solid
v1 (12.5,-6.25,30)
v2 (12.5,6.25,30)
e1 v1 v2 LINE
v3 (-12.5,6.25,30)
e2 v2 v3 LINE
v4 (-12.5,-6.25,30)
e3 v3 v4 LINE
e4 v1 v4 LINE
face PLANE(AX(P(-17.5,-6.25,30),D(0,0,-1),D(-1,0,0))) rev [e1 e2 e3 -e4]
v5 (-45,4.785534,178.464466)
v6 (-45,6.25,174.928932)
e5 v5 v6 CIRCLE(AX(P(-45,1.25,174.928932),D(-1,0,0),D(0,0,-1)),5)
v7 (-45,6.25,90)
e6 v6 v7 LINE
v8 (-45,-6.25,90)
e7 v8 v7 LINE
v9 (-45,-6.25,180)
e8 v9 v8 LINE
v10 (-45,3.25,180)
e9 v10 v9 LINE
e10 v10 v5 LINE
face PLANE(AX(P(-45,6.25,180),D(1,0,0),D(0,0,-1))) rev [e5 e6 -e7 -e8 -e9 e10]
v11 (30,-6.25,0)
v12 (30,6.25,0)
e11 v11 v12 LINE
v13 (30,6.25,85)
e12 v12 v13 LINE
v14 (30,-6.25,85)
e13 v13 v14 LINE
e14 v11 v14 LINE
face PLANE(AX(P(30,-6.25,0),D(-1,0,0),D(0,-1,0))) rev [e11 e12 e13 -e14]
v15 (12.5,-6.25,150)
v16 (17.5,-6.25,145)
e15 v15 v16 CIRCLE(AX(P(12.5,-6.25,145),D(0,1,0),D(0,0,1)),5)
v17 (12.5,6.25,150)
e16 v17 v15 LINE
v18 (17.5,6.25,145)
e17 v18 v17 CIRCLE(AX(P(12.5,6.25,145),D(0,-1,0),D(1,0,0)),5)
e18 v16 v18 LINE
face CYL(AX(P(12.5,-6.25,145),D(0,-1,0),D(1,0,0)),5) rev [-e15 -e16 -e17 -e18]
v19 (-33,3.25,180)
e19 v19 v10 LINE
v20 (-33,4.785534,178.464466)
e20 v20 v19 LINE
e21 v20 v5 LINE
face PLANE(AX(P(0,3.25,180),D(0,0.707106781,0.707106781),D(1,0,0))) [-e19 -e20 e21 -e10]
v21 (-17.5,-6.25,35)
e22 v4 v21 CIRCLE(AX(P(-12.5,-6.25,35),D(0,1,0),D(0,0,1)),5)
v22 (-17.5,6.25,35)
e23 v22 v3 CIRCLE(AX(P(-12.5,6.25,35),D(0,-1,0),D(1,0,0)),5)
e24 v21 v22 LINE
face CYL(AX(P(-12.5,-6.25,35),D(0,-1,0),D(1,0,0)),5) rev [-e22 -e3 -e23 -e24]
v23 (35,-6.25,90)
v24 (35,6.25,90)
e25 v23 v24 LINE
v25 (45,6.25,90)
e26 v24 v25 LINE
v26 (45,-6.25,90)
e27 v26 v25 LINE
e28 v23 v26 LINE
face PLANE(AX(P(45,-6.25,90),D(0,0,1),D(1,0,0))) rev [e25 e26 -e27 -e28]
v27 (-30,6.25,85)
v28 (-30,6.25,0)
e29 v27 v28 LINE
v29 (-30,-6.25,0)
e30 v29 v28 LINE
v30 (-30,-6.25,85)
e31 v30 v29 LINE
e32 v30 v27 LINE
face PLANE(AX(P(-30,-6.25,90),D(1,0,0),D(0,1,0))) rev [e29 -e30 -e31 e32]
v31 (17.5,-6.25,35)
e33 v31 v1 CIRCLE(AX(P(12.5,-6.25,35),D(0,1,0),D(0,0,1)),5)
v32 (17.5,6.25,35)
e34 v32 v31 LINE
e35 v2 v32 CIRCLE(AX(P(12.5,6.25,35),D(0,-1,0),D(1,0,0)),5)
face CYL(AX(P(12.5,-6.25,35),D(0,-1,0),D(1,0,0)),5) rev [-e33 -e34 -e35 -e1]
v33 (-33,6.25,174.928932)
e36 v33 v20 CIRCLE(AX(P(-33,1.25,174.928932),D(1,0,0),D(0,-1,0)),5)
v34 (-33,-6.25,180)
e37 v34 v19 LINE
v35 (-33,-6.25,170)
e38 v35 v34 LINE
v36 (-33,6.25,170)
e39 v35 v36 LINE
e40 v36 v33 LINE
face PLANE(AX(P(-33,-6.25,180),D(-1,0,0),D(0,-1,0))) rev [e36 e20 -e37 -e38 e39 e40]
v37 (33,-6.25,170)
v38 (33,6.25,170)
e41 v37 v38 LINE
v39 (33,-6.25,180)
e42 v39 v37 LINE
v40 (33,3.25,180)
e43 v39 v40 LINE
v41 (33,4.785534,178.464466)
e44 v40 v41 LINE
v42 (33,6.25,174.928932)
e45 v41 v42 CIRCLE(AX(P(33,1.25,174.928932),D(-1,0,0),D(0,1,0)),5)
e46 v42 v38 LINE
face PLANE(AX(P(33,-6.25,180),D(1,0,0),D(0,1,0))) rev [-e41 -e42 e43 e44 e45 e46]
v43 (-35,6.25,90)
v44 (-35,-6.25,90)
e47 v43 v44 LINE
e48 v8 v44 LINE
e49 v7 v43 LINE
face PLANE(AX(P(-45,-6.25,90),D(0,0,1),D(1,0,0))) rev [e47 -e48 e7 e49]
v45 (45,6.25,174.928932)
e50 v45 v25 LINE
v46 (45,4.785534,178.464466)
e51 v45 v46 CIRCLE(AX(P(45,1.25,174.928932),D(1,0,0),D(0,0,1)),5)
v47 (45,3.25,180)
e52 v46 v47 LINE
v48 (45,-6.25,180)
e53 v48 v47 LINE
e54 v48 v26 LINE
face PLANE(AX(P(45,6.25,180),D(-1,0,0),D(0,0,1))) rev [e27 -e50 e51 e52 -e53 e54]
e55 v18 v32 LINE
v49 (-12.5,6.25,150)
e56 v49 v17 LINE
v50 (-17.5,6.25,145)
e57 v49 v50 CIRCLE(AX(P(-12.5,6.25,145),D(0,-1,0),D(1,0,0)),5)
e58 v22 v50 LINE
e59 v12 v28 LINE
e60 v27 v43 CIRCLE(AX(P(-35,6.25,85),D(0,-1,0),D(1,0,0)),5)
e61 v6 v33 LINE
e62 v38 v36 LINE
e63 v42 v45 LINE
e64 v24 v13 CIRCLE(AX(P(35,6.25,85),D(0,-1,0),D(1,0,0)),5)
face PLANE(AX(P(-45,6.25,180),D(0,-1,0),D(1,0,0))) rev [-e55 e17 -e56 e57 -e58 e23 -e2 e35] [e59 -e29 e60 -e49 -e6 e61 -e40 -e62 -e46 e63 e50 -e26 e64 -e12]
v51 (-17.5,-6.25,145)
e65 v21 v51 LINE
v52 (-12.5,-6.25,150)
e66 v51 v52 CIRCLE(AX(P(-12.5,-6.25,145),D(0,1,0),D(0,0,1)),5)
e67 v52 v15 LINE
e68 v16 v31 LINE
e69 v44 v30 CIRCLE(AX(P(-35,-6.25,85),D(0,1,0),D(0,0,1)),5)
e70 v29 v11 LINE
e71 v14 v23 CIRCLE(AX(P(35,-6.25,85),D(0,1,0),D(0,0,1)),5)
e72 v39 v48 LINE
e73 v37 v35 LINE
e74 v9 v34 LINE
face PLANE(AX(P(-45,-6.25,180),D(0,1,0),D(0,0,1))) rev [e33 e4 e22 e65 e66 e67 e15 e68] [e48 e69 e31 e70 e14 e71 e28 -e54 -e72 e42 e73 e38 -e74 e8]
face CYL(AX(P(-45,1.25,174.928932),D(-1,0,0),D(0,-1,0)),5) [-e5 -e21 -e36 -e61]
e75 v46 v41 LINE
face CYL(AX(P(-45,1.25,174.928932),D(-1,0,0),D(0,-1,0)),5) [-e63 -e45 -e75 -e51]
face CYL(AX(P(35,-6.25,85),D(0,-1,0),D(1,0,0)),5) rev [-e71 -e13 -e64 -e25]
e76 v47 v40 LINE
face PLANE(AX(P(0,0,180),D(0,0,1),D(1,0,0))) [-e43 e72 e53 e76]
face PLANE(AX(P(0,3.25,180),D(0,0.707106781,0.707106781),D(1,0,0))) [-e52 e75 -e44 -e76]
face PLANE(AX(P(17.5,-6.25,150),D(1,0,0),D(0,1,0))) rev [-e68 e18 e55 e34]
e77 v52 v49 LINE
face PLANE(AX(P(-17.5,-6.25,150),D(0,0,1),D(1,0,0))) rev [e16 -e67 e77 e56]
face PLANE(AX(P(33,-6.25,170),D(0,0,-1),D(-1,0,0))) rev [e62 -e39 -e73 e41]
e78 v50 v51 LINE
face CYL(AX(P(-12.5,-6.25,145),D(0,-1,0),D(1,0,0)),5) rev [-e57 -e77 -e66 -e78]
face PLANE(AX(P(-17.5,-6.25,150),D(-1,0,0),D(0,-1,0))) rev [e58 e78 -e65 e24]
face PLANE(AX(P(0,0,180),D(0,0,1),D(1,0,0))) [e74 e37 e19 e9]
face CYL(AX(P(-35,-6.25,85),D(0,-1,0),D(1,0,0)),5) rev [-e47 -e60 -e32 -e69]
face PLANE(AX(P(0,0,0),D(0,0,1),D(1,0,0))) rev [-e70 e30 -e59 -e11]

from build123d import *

# Parameters (mm, degrees)
SKETCH1_W           = 90
SKETCH1_H           = 12.5
BOSS_EXTRUDE1_DEPTH = 180
SKETCH2_W           = 66
SKETCH2_H           = 10
CUT_EXTRUDE1_DEPTH  = 186.960345235
CHAMFER1_SIZE       = 3
FILLET1_R           = 5
SKETCH3_W           = 15
SKETCH3_H           = 90
CUT_EXTRUDE2_DEPTH  = 186.960345235
SKETCH4_W           = 35
SKETCH4_H           = 120
CUT_EXTRUDE3_DEPTH  = 186.960345235
FILLET2_R           = 5
FILLET3_R           = 5


with BuildPart() as part:
    # Sketch1 → Boss-Extrude1 (new body)
    with BuildSketch(Plane.XY):
        Rectangle(SKETCH1_W, SKETCH1_H)
    extrude(amount=BOSS_EXTRUDE1_DEPTH)

    # Sketch2 → Cut-Extrude1 (cut, through all)
    with BuildSketch(Plane(origin=(0, 6.25, 0), x_dir=(1, 0, 0), z_dir=(0, 1, 0))):
        with Locations((0, -175)):
            Rectangle(SKETCH2_W, SKETCH2_H)
    extrude(amount=-CUT_EXTRUDE1_DEPTH, mode=Mode.SUBTRACT)

    # Chamfer1
    chamfer1_edges = [part.edges().sort_by_distance(p)[0] for p in [
        (39, 6.25, 180),
        (-39, 6.25, 180),
    ]]
    chamfer(chamfer1_edges, length=CHAMFER1_SIZE)

    # Fillet1
    fillet1_edges = [part.edges().sort_by_distance(p)[0] for p in [
        (39, 6.25, 177),
        (-39, 6.25, 177),
    ]]
    fillet(fillet1_edges, radius=FILLET1_R)

    # Sketch3 → Cut-Extrude2 (cut, through all)
    with BuildSketch(Plane(origin=(0, 6.25, 0), x_dir=(1, 0, 0), z_dir=(0, 1, 0))):
        with Locations((37.5, -45)):
            Rectangle(SKETCH3_W, SKETCH3_H)
        with Locations((-37.5, -45)):
            Rectangle(SKETCH3_W, SKETCH3_H)
    extrude(amount=-CUT_EXTRUDE2_DEPTH, mode=Mode.SUBTRACT)

    # Sketch4 → Cut-Extrude3 (cut, through all)
    with BuildSketch(Plane(origin=(0, 6.25, 0), x_dir=(1, 0, 0), z_dir=(0, 1, 0))):
        with Locations((0, -90)):
            Rectangle(SKETCH4_W, SKETCH4_H)
    extrude(amount=-CUT_EXTRUDE3_DEPTH, mode=Mode.SUBTRACT)

    # Fillet2
    fillet2_edges = [part.edges().sort_by_distance(p)[0] for p in [
        (-17.5, 0, 150),
        (-17.5, 0, 30),
        (17.5, 0, 30),
        (17.5, 0, 150),
    ]]
    fillet(fillet2_edges, radius=FILLET2_R)

    # Fillet3
    fillet3_edges = [part.edges().sort_by_distance(p)[0] for p in [
        (30, 0, 90),
        (-30, 0, 90),
    ]]
    fillet(fillet3_edges, radius=FILLET3_R)


solid = part.part
